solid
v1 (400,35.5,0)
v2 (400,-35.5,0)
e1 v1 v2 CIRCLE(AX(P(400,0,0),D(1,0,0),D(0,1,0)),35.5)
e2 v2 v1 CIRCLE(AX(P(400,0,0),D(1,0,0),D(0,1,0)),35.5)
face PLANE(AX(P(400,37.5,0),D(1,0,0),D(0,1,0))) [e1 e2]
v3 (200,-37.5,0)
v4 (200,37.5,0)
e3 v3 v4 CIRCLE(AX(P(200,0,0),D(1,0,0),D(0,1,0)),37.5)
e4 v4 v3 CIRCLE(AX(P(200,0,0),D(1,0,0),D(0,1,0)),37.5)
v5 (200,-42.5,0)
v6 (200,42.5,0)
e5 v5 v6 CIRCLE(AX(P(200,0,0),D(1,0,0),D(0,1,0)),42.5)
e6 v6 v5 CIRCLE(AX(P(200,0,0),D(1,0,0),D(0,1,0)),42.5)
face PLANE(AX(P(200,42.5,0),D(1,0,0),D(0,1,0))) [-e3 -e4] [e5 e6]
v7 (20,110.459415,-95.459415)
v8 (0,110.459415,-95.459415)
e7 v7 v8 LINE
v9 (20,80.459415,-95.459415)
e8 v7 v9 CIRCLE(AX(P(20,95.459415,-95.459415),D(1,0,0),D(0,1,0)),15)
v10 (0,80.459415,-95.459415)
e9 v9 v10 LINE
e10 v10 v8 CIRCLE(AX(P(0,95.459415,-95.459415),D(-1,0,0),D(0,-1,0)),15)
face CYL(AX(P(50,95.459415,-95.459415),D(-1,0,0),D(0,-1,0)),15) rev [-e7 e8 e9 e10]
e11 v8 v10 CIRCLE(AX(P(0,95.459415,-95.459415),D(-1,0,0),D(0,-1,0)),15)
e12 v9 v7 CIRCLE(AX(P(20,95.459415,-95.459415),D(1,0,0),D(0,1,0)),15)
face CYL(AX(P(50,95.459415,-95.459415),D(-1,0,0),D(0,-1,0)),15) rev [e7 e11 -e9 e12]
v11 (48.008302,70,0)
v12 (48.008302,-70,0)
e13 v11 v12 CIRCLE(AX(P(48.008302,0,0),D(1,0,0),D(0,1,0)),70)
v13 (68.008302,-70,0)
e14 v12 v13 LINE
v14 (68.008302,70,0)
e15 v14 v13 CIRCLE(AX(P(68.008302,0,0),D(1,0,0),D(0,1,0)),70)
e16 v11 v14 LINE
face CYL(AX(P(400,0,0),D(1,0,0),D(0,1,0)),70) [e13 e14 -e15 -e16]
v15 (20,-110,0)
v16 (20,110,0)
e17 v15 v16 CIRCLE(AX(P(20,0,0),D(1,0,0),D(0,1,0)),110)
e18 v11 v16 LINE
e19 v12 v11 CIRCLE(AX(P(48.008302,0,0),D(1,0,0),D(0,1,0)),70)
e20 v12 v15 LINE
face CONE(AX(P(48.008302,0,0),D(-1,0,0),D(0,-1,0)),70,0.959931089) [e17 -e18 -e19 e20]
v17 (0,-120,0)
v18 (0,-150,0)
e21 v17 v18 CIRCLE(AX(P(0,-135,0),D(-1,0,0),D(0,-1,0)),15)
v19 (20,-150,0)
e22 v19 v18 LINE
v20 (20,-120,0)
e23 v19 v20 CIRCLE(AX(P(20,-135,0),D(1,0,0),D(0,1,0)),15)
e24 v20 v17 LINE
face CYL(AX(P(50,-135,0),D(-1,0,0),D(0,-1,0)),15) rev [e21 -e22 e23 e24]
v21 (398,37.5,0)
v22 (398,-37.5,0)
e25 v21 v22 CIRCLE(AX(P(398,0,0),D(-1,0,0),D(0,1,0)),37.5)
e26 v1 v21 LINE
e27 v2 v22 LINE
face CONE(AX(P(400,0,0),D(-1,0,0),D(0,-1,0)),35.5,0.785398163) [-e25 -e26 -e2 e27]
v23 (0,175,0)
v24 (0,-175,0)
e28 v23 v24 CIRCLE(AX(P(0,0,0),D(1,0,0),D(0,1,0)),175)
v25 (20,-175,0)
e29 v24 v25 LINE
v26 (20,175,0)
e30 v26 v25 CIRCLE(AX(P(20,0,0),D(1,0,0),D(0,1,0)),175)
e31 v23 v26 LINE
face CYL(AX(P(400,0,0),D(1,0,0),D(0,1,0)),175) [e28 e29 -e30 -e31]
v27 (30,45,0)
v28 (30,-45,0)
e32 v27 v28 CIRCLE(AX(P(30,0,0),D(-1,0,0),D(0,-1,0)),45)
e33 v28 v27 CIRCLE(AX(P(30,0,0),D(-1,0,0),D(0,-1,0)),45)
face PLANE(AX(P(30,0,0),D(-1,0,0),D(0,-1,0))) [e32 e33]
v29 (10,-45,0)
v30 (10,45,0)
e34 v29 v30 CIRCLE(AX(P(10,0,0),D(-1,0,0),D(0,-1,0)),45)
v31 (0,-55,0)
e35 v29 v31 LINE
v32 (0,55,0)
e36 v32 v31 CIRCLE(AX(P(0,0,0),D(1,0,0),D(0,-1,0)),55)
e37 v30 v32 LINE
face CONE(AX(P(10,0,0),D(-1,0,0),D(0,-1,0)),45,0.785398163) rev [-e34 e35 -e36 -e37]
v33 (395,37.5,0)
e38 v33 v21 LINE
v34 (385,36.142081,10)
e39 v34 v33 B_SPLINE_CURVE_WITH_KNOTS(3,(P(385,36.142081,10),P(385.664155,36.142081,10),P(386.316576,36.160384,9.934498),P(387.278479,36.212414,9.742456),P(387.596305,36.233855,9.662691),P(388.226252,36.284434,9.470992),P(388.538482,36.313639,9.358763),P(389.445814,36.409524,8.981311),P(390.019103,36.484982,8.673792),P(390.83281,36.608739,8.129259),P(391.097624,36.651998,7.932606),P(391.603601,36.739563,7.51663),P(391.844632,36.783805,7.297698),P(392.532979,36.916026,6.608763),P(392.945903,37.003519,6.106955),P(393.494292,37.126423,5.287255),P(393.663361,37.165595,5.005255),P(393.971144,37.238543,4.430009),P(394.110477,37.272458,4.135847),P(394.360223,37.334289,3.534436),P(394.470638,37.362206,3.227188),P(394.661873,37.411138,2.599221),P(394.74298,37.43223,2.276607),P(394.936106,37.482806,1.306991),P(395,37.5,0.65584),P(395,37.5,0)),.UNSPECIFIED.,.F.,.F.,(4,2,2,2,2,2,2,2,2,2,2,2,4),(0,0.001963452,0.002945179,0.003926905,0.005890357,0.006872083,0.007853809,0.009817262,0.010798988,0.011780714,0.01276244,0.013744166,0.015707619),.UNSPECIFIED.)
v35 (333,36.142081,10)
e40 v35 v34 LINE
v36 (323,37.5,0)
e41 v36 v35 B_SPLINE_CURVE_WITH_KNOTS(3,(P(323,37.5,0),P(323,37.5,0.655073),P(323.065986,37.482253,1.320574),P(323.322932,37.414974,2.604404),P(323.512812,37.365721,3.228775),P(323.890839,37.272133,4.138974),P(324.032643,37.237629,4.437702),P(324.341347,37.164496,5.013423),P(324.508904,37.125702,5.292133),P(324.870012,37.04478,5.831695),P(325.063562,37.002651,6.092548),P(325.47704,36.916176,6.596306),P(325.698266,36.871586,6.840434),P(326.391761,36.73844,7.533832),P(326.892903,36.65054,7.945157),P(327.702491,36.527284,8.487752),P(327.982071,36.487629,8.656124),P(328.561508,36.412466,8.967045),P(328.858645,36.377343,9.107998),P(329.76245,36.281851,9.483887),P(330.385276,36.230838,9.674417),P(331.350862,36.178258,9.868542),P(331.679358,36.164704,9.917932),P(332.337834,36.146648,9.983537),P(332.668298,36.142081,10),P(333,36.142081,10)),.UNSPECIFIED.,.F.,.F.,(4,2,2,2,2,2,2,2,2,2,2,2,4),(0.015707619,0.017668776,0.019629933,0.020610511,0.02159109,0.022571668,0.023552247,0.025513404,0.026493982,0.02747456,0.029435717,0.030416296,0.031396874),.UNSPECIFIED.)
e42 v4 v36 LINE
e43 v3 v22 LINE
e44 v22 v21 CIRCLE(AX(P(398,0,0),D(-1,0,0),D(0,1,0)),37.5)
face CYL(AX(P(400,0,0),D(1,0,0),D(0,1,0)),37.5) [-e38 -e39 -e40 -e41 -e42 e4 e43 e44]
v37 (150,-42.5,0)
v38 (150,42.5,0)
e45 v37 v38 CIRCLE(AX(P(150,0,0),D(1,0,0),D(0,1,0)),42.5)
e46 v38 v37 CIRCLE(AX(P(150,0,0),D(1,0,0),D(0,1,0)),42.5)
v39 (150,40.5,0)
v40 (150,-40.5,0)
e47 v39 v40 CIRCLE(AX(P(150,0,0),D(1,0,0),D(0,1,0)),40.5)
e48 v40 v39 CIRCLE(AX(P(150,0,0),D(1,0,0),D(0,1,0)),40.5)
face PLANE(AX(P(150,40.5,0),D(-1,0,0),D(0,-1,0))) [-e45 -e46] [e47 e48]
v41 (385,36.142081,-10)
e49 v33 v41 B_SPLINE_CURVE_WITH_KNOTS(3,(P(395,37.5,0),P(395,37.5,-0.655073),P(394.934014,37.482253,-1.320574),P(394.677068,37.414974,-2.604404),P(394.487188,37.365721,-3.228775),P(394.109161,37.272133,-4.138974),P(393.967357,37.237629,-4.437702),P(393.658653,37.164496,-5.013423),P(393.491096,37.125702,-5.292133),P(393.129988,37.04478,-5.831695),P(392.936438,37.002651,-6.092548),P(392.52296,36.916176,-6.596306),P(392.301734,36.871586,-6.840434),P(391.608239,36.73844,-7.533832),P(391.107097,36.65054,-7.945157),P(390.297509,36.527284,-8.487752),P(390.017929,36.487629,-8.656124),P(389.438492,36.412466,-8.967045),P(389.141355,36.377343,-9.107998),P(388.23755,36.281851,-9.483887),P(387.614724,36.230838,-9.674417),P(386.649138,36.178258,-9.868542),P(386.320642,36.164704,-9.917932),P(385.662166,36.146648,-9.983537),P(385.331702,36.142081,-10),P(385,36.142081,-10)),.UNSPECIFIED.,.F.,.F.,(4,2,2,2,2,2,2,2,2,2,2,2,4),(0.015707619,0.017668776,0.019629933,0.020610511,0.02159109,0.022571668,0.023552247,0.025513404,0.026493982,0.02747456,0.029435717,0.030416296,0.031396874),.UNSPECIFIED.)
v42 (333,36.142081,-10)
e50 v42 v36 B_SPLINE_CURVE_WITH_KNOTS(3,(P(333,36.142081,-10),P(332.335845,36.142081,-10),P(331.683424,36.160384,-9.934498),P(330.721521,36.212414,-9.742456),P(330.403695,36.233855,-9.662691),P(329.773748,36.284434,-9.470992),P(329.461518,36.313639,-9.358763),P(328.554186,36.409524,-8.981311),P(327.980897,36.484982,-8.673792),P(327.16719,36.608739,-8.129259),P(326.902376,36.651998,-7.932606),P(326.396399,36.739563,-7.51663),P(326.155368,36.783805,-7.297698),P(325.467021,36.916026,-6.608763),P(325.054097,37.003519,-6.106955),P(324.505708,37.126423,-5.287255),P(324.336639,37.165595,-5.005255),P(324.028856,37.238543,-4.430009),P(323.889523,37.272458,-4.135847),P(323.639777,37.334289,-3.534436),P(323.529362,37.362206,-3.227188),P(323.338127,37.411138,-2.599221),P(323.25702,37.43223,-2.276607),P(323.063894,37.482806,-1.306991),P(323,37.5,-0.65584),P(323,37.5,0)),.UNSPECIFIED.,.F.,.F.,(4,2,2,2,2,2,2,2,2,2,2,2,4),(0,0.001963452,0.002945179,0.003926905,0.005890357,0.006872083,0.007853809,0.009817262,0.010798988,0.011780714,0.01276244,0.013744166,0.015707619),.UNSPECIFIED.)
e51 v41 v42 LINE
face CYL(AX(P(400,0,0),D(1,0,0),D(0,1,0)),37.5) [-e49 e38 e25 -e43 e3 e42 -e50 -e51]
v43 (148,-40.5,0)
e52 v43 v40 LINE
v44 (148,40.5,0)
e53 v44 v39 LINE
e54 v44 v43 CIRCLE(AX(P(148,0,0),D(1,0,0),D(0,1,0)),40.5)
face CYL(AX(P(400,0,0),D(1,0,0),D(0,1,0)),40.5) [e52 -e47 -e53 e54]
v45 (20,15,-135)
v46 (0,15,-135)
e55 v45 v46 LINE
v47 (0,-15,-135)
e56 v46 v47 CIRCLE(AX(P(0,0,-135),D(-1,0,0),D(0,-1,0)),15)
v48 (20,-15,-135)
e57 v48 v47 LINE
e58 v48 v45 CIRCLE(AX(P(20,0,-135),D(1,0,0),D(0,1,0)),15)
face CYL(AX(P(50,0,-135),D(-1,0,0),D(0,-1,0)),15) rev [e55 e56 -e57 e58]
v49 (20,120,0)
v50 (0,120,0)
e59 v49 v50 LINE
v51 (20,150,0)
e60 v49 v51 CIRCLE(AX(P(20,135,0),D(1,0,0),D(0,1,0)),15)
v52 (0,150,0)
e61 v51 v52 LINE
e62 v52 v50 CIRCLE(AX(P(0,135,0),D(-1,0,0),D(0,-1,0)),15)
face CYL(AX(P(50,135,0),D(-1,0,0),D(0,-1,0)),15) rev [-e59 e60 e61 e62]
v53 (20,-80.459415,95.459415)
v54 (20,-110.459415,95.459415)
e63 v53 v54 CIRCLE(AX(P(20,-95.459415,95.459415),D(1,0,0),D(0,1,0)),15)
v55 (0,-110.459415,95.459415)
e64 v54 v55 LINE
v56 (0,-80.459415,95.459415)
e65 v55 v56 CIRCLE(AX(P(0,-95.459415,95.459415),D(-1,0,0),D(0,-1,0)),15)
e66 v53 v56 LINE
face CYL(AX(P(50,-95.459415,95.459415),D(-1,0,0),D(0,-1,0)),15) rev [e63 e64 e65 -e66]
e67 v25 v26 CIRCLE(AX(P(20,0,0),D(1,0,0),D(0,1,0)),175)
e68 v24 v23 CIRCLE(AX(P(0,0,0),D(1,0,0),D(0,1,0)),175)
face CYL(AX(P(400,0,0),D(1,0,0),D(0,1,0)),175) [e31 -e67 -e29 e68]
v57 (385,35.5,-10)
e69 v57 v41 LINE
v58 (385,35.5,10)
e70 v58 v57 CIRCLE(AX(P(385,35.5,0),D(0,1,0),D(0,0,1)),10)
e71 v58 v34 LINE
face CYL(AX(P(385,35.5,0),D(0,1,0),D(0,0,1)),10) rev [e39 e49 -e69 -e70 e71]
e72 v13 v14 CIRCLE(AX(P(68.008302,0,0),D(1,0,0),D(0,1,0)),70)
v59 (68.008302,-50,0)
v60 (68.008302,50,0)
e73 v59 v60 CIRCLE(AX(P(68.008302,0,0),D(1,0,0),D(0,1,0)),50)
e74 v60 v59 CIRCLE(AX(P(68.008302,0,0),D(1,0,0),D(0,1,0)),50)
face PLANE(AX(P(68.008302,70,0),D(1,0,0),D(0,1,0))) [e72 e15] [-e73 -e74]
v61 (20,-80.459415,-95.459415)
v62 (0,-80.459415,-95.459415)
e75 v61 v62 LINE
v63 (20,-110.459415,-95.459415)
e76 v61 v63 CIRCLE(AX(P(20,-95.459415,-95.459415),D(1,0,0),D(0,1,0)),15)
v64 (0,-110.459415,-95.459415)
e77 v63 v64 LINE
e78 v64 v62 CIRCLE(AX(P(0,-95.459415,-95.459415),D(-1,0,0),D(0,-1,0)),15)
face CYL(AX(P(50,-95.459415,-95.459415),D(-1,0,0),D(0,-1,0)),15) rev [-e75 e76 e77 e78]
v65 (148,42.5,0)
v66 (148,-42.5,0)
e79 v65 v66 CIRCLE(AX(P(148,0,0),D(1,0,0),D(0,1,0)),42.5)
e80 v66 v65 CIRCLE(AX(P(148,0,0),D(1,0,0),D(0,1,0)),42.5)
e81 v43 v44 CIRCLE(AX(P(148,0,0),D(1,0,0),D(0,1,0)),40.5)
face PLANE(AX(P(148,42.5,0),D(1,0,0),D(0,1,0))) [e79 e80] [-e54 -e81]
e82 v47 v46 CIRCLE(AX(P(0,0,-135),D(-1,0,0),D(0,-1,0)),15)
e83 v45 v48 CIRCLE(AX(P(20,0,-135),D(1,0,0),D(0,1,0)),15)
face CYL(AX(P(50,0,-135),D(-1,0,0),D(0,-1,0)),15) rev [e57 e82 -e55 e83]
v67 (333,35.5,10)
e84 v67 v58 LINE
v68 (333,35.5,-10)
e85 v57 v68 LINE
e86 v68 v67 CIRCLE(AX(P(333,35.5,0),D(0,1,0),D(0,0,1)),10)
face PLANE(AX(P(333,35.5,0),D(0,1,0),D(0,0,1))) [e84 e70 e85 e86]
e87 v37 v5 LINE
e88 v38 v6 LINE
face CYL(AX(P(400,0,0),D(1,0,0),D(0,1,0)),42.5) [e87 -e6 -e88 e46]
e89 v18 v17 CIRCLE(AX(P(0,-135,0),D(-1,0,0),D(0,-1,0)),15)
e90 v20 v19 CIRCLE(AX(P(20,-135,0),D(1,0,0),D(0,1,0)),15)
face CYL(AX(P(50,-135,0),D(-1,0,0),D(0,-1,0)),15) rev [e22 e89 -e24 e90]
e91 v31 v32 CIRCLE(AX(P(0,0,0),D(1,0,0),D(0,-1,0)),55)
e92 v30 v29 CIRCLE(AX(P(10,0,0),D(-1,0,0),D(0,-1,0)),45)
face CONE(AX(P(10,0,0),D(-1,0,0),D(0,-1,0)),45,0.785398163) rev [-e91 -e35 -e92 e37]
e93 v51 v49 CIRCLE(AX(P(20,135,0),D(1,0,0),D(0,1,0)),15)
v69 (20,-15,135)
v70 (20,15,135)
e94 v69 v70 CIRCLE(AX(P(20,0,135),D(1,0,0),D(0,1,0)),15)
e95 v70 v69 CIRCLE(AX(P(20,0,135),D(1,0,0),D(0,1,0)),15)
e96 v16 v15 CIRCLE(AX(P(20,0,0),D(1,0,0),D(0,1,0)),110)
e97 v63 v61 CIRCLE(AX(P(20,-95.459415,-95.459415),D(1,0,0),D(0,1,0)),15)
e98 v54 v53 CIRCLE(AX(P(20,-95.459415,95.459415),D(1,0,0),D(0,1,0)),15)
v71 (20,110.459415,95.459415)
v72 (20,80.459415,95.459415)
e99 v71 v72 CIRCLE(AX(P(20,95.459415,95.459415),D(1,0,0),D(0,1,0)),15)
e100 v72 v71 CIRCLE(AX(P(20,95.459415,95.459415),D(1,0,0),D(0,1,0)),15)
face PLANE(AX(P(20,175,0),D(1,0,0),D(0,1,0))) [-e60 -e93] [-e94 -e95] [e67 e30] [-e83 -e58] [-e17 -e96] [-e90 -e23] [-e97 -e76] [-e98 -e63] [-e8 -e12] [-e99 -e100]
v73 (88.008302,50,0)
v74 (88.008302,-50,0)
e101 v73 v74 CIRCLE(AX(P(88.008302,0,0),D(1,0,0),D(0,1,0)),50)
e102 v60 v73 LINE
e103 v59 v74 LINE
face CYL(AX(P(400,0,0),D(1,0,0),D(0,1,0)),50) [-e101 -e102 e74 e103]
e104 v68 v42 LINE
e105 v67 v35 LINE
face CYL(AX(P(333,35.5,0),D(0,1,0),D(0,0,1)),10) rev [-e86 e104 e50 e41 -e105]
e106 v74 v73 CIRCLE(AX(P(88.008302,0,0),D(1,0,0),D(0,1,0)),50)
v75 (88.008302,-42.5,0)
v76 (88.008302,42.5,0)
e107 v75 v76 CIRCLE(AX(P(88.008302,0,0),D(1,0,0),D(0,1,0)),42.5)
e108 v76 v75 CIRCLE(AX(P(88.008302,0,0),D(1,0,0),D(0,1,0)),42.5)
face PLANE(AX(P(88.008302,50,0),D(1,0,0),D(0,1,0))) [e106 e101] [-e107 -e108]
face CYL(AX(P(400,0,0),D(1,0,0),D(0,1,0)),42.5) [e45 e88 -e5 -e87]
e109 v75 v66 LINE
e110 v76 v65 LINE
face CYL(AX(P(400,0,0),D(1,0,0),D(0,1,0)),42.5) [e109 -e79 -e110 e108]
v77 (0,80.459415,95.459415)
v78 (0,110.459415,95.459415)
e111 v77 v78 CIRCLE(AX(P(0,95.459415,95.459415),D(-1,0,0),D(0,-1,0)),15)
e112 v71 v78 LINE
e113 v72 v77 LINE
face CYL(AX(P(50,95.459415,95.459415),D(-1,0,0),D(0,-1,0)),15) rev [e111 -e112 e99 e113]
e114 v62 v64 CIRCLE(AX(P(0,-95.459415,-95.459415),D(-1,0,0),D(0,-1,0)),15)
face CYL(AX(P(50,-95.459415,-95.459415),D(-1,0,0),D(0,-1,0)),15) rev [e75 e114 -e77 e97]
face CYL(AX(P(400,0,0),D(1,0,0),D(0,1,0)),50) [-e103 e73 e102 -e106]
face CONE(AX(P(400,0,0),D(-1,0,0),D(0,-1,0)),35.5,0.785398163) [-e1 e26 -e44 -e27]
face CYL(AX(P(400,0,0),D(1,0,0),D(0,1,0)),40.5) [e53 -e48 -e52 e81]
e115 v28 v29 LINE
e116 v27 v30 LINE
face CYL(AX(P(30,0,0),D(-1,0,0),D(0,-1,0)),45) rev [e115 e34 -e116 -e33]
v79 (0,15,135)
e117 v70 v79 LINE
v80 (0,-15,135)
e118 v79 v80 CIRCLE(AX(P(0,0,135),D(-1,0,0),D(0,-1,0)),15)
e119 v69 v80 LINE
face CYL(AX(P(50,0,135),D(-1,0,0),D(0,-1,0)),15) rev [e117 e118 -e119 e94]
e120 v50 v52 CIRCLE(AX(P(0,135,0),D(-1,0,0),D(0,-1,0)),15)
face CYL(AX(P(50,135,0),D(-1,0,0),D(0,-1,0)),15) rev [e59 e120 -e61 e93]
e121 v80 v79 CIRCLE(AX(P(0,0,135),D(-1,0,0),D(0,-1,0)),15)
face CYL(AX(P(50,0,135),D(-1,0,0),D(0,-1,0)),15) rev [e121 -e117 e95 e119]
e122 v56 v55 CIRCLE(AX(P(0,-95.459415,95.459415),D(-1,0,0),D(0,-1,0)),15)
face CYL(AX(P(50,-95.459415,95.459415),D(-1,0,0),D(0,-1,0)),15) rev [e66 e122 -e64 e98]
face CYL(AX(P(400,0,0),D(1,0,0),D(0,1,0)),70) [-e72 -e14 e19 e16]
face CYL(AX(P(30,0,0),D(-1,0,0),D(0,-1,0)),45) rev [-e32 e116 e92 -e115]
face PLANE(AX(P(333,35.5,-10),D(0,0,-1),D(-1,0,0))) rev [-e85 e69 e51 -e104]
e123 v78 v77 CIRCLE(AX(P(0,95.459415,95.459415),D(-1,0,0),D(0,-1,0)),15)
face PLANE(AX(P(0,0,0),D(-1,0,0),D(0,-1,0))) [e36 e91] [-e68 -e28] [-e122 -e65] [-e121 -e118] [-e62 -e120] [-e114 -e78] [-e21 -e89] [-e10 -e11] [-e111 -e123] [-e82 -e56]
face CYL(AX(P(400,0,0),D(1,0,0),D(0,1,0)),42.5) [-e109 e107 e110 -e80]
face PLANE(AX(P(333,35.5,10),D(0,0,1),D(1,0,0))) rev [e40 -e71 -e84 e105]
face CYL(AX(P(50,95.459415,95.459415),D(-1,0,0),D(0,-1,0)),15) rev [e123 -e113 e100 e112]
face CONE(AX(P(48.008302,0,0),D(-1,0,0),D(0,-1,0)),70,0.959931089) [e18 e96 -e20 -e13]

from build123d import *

# Parameters (mm, degrees)
SKETCH_2_R          = 45
CUT_EXTRUDE_1_DEPTH = 30
CHAMFER_1_SIZE      = 10
CUT_EXTRUDE_2_DEPTH = 2
CHAMFER_2_SIZE      = 2
SKETCH_4_R          = 15
CUT_EXTRUDE_3_DEPTH = 50


with BuildPart() as part:
    # 草图1 → 旋转1 (revolve)
    with BuildSketch(Plane.XY):
        Polygon((0, 0), (0, 175), (20, 175), (20, 110), (48.008301528, 70), (68.008301528, 70), (68.008301528, 50), (88.008301528, 50), (88.008301528, 42.5), (148, 42.5), (148, 40.5), (150, 40.5), (150, 42.5), (200, 42.5), (200, 37.5), (400, 37.5), (400, 0), align=None)
    revolve(axis=Axis((400, 0, 0), (-1, 0, 0)))

    # 草图2 → 切除-拉伸1 (cut)
    with BuildSketch(Plane.ZY):
        with Locations(Location((0, 0, 0), (0, 0, 270))):
            Circle(SKETCH_2_R)
    extrude(amount=-CUT_EXTRUDE_1_DEPTH, mode=Mode.SUBTRACT)

    # 倒角1
    chamfer_1_edges = [part.edges().sort_by_distance(p)[0] for p in [
        (0, 45, 0),
    ]]
    chamfer(chamfer_1_edges, length=CHAMFER_1_SIZE)

    # 草图3 → 切除-拉伸2 (cut)
    with BuildSketch(Plane(origin=(0, 37.5, 0), x_dir=(1, 0, 0), z_dir=(0, 1, 0))):
        with BuildLine():
            Line((333, 10), (385, 10))
            ThreePointArc((385, 10), (395, 0), (385, -10))
            Line((385, -10), (333, -10))
            ThreePointArc((333, -10), (323, 0), (333, 10))
        make_face()
    extrude(amount=-CUT_EXTRUDE_2_DEPTH, mode=Mode.SUBTRACT)

    # 倒角2
    chamfer_2_edges = [part.edges().sort_by_distance(p)[0] for p in [
        (400, -37.5, 0),
    ]]
    chamfer(chamfer_2_edges, length=CHAMFER_2_SIZE)

    # 草图4 → 切除-拉伸3 (cut)
    with BuildSketch(Plane.ZY):
        with Locations(Location((0, 135, 0), (0, 0, 270))):
            Circle(SKETCH_4_R)
        with Locations(Location((95.45941546, 95.45941546, 0), (0, 0, 270))):
            Circle(SKETCH_4_R)
        with Locations(Location((135, 0, 0), (0, 0, 270))):
            Circle(SKETCH_4_R)
        with Locations(Location((95.45941546, -95.45941546, 0), (0, 0, 270))):
            Circle(SKETCH_4_R)
        with Locations(Location((0, -135, 0), (0, 0, 270))):
            Circle(SKETCH_4_R)
        with Locations(Location((-95.45941546, -95.45941546, 0), (0, 0, 270))):
            Circle(SKETCH_4_R)
        with Locations(Location((-135, 0, 0), (0, 0, 270))):
            Circle(SKETCH_4_R)
        with Locations(Location((-95.45941546, 95.45941546, 0), (0, 0, 270))):
            Circle(SKETCH_4_R)
    extrude(amount=-CUT_EXTRUDE_3_DEPTH, mode=Mode.SUBTRACT)


solid = part.part
